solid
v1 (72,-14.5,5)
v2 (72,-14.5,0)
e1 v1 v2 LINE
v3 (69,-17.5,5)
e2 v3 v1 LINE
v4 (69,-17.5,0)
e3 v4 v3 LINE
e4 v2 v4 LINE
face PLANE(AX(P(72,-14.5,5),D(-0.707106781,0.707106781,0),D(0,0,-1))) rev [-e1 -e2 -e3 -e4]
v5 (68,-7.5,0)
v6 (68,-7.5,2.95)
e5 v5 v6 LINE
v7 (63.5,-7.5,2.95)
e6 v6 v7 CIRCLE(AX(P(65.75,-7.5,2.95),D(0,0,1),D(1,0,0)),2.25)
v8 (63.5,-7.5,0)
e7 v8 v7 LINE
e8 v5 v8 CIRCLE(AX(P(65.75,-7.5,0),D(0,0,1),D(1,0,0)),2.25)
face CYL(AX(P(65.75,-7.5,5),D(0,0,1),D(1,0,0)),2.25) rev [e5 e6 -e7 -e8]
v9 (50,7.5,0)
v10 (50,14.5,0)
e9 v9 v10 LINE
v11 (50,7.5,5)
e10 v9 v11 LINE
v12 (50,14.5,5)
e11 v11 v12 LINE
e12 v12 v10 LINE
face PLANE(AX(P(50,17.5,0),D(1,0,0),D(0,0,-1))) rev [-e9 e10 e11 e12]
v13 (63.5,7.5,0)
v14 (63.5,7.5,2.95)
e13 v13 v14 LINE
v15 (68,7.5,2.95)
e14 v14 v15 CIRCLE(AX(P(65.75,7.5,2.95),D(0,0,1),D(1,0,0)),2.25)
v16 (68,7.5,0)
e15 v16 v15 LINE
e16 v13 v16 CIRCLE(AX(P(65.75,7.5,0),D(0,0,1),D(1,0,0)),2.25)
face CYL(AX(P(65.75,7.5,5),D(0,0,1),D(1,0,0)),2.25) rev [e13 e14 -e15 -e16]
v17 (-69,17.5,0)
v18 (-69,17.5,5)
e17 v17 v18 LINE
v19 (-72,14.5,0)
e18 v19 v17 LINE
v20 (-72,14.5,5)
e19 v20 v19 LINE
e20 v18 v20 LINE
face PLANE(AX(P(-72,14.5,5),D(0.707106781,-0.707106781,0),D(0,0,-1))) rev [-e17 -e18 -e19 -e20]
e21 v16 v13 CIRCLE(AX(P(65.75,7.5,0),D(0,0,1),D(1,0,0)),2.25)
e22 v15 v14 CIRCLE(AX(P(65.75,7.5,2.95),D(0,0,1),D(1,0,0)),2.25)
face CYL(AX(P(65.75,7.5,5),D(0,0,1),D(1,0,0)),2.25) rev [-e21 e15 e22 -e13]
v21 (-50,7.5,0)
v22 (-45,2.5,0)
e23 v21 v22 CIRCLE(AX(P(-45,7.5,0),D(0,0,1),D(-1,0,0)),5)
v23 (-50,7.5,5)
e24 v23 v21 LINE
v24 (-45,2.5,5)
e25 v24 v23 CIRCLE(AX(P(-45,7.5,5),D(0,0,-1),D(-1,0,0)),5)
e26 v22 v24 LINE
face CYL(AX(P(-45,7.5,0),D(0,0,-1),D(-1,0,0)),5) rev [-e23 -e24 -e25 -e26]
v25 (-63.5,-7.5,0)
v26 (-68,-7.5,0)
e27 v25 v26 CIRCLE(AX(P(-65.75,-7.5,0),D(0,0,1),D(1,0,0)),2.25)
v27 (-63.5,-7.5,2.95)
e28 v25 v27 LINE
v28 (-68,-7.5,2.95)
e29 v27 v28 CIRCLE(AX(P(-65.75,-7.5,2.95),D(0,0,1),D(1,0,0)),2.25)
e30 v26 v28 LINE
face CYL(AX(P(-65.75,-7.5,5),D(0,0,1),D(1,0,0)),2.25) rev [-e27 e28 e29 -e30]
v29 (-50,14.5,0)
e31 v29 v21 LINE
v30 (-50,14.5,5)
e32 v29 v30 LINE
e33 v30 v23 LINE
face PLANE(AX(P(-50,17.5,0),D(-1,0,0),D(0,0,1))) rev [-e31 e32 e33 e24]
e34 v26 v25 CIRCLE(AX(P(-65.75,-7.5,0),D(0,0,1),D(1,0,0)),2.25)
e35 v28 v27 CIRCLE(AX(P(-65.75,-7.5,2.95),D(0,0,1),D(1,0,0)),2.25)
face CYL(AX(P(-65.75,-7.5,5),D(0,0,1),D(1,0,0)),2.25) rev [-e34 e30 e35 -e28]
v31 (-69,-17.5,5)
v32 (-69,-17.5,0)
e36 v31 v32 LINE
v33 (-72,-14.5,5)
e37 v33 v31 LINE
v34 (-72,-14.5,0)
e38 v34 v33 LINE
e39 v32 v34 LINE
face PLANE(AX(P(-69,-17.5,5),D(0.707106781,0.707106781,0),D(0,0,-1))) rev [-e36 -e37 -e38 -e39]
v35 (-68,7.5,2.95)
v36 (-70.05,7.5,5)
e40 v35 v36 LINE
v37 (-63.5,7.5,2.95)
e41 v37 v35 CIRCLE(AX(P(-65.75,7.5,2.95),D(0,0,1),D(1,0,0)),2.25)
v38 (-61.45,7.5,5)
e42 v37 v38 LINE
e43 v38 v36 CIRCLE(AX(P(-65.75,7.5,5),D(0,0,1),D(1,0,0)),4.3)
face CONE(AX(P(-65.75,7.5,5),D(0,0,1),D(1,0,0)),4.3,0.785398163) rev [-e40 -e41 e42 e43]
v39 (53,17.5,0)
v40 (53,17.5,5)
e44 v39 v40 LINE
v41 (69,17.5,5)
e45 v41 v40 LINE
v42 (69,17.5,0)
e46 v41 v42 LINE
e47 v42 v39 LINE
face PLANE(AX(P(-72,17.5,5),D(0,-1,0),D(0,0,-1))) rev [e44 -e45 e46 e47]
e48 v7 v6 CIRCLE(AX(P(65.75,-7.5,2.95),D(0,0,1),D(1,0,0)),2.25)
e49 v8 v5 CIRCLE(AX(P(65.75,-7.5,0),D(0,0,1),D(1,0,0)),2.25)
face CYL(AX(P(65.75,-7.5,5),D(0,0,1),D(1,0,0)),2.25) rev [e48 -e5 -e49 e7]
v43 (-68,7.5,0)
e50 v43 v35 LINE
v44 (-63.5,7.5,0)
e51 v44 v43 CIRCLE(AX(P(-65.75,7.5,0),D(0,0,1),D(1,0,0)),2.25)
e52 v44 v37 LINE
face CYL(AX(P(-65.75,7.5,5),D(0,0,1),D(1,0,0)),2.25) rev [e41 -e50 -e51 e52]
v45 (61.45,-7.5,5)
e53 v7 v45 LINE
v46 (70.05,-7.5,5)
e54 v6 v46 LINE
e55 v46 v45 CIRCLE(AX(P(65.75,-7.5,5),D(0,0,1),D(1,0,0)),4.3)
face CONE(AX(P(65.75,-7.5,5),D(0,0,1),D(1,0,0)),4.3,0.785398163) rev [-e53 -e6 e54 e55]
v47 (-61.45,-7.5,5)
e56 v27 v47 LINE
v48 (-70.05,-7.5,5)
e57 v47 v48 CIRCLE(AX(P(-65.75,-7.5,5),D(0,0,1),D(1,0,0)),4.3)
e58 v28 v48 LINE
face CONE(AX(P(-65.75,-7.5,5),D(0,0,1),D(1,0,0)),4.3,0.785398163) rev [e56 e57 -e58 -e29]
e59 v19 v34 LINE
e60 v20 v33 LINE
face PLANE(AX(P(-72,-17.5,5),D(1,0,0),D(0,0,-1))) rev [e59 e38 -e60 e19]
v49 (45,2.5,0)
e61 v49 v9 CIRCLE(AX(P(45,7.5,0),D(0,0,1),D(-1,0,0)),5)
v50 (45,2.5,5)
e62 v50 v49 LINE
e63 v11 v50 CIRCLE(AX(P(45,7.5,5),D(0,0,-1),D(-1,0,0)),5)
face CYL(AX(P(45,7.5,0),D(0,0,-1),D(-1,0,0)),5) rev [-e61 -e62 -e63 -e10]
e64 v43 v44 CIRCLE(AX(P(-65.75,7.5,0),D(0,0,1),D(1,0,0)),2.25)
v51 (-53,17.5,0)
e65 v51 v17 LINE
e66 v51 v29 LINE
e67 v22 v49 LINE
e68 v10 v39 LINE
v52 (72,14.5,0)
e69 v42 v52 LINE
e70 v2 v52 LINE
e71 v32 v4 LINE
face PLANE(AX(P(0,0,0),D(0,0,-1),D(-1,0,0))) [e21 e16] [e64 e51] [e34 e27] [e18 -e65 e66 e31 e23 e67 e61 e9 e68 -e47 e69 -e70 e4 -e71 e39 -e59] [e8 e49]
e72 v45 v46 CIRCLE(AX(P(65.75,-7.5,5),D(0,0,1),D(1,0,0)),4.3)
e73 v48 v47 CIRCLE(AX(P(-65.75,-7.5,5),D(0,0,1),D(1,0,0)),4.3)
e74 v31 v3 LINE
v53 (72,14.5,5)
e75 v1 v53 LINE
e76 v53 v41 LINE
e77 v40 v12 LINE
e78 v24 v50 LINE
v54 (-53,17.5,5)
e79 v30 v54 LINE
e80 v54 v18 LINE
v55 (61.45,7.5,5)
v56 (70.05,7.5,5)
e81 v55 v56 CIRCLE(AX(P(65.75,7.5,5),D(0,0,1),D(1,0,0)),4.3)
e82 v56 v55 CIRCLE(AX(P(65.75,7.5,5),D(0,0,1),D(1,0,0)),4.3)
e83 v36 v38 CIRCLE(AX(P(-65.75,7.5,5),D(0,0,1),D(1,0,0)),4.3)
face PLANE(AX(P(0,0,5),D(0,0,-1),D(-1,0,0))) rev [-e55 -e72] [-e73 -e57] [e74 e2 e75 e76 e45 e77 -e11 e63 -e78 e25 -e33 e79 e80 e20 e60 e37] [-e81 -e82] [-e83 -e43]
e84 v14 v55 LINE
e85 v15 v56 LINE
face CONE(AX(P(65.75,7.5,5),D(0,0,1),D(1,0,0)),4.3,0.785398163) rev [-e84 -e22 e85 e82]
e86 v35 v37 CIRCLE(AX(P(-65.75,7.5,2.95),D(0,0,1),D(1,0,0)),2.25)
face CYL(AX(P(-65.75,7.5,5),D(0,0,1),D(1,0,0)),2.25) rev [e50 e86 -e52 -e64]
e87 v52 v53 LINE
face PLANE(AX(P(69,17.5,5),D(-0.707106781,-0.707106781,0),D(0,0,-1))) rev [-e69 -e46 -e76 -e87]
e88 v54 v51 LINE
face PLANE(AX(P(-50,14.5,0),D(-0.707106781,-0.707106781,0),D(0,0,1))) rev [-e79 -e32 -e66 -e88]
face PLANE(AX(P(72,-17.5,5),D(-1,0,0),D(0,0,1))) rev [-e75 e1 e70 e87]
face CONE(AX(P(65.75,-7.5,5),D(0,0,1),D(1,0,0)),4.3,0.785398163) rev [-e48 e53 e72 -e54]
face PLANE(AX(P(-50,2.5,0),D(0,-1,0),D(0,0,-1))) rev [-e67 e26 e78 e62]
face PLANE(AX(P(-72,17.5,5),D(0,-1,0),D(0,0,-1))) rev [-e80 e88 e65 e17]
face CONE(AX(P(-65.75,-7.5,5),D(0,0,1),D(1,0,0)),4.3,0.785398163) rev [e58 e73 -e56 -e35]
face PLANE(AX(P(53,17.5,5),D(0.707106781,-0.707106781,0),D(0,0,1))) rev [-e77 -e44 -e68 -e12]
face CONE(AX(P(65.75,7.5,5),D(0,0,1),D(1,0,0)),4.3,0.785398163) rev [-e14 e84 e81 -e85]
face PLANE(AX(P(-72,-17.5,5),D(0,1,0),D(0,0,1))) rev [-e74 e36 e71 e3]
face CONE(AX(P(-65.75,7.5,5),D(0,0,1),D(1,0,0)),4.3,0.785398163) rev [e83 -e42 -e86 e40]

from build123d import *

# Parameters (mm, degrees)
SKETCH_1_W                = 144
SKETCH_1_H                = 35
EXTRUDE_1_DEPTH           = 5
HOLE_WIZARD_1_D           = 4.5
HOLE_WIZARD_1_CSINK_D     = 8.6
HOLE_WIZARD_1_CSINK_ANGLE = 90
SKETCH_4_W                = 100
SKETCH_4_H                = 15
CUT_EXTRUDE_1_DEPTH       = 75.264729179
CHAMFER_1_SIZE            = 3
FILLET_1_R                = 5


with BuildPart() as part:
    # 草图1 → 凸台-拉伸1 (new body)
    with BuildSketch(Plane.XY):
        Rectangle(SKETCH_1_W, SKETCH_1_H)
    extrude(amount=EXTRUDE_1_DEPTH)

    # 打孔尺寸根据十字槽沉头木螺钉的类型1 (through all)
    with Locations(Plane.XY.offset(5)):
        with Locations((-65.75, 7.5), (-65.75, -7.5), (65.75, 7.5), (65.75, -7.5)):
            CounterSinkHole(HOLE_WIZARD_1_D / 2, HOLE_WIZARD_1_CSINK_D / 2, counter_sink_angle=HOLE_WIZARD_1_CSINK_ANGLE)

    # 草图4 → 切除-拉伸1 (cut, through all)
    with BuildSketch(Plane.XY.offset(5)):
        with Locations((0, 10)):
            Rectangle(SKETCH_4_W, SKETCH_4_H)
    extrude(amount=-CUT_EXTRUDE_1_DEPTH, mode=Mode.SUBTRACT)

    # 倒角1
    chamfer_1_edges = [part.edges().sort_by_distance(p)[0] for p in [
        (-50, 17.5, 2.5),
        (50, 17.5, 2.5),
        (72, -17.5, 2.5),
        (-72, -17.5, 2.5),
        (-72, 17.5, 2.5),
        (72, 17.5, 2.5),
    ]]
    chamfer(chamfer_1_edges, length=CHAMFER_1_SIZE)

    # 圆角1
    fillet_1_edges = [part.edges().sort_by_distance(p)[0] for p in [
        (-50, 2.5, 2.5),
        (50, 2.5, 2.5),
    ]]
    fillet(fillet_1_edges, radius=FILLET_1_R)


solid = part.part
